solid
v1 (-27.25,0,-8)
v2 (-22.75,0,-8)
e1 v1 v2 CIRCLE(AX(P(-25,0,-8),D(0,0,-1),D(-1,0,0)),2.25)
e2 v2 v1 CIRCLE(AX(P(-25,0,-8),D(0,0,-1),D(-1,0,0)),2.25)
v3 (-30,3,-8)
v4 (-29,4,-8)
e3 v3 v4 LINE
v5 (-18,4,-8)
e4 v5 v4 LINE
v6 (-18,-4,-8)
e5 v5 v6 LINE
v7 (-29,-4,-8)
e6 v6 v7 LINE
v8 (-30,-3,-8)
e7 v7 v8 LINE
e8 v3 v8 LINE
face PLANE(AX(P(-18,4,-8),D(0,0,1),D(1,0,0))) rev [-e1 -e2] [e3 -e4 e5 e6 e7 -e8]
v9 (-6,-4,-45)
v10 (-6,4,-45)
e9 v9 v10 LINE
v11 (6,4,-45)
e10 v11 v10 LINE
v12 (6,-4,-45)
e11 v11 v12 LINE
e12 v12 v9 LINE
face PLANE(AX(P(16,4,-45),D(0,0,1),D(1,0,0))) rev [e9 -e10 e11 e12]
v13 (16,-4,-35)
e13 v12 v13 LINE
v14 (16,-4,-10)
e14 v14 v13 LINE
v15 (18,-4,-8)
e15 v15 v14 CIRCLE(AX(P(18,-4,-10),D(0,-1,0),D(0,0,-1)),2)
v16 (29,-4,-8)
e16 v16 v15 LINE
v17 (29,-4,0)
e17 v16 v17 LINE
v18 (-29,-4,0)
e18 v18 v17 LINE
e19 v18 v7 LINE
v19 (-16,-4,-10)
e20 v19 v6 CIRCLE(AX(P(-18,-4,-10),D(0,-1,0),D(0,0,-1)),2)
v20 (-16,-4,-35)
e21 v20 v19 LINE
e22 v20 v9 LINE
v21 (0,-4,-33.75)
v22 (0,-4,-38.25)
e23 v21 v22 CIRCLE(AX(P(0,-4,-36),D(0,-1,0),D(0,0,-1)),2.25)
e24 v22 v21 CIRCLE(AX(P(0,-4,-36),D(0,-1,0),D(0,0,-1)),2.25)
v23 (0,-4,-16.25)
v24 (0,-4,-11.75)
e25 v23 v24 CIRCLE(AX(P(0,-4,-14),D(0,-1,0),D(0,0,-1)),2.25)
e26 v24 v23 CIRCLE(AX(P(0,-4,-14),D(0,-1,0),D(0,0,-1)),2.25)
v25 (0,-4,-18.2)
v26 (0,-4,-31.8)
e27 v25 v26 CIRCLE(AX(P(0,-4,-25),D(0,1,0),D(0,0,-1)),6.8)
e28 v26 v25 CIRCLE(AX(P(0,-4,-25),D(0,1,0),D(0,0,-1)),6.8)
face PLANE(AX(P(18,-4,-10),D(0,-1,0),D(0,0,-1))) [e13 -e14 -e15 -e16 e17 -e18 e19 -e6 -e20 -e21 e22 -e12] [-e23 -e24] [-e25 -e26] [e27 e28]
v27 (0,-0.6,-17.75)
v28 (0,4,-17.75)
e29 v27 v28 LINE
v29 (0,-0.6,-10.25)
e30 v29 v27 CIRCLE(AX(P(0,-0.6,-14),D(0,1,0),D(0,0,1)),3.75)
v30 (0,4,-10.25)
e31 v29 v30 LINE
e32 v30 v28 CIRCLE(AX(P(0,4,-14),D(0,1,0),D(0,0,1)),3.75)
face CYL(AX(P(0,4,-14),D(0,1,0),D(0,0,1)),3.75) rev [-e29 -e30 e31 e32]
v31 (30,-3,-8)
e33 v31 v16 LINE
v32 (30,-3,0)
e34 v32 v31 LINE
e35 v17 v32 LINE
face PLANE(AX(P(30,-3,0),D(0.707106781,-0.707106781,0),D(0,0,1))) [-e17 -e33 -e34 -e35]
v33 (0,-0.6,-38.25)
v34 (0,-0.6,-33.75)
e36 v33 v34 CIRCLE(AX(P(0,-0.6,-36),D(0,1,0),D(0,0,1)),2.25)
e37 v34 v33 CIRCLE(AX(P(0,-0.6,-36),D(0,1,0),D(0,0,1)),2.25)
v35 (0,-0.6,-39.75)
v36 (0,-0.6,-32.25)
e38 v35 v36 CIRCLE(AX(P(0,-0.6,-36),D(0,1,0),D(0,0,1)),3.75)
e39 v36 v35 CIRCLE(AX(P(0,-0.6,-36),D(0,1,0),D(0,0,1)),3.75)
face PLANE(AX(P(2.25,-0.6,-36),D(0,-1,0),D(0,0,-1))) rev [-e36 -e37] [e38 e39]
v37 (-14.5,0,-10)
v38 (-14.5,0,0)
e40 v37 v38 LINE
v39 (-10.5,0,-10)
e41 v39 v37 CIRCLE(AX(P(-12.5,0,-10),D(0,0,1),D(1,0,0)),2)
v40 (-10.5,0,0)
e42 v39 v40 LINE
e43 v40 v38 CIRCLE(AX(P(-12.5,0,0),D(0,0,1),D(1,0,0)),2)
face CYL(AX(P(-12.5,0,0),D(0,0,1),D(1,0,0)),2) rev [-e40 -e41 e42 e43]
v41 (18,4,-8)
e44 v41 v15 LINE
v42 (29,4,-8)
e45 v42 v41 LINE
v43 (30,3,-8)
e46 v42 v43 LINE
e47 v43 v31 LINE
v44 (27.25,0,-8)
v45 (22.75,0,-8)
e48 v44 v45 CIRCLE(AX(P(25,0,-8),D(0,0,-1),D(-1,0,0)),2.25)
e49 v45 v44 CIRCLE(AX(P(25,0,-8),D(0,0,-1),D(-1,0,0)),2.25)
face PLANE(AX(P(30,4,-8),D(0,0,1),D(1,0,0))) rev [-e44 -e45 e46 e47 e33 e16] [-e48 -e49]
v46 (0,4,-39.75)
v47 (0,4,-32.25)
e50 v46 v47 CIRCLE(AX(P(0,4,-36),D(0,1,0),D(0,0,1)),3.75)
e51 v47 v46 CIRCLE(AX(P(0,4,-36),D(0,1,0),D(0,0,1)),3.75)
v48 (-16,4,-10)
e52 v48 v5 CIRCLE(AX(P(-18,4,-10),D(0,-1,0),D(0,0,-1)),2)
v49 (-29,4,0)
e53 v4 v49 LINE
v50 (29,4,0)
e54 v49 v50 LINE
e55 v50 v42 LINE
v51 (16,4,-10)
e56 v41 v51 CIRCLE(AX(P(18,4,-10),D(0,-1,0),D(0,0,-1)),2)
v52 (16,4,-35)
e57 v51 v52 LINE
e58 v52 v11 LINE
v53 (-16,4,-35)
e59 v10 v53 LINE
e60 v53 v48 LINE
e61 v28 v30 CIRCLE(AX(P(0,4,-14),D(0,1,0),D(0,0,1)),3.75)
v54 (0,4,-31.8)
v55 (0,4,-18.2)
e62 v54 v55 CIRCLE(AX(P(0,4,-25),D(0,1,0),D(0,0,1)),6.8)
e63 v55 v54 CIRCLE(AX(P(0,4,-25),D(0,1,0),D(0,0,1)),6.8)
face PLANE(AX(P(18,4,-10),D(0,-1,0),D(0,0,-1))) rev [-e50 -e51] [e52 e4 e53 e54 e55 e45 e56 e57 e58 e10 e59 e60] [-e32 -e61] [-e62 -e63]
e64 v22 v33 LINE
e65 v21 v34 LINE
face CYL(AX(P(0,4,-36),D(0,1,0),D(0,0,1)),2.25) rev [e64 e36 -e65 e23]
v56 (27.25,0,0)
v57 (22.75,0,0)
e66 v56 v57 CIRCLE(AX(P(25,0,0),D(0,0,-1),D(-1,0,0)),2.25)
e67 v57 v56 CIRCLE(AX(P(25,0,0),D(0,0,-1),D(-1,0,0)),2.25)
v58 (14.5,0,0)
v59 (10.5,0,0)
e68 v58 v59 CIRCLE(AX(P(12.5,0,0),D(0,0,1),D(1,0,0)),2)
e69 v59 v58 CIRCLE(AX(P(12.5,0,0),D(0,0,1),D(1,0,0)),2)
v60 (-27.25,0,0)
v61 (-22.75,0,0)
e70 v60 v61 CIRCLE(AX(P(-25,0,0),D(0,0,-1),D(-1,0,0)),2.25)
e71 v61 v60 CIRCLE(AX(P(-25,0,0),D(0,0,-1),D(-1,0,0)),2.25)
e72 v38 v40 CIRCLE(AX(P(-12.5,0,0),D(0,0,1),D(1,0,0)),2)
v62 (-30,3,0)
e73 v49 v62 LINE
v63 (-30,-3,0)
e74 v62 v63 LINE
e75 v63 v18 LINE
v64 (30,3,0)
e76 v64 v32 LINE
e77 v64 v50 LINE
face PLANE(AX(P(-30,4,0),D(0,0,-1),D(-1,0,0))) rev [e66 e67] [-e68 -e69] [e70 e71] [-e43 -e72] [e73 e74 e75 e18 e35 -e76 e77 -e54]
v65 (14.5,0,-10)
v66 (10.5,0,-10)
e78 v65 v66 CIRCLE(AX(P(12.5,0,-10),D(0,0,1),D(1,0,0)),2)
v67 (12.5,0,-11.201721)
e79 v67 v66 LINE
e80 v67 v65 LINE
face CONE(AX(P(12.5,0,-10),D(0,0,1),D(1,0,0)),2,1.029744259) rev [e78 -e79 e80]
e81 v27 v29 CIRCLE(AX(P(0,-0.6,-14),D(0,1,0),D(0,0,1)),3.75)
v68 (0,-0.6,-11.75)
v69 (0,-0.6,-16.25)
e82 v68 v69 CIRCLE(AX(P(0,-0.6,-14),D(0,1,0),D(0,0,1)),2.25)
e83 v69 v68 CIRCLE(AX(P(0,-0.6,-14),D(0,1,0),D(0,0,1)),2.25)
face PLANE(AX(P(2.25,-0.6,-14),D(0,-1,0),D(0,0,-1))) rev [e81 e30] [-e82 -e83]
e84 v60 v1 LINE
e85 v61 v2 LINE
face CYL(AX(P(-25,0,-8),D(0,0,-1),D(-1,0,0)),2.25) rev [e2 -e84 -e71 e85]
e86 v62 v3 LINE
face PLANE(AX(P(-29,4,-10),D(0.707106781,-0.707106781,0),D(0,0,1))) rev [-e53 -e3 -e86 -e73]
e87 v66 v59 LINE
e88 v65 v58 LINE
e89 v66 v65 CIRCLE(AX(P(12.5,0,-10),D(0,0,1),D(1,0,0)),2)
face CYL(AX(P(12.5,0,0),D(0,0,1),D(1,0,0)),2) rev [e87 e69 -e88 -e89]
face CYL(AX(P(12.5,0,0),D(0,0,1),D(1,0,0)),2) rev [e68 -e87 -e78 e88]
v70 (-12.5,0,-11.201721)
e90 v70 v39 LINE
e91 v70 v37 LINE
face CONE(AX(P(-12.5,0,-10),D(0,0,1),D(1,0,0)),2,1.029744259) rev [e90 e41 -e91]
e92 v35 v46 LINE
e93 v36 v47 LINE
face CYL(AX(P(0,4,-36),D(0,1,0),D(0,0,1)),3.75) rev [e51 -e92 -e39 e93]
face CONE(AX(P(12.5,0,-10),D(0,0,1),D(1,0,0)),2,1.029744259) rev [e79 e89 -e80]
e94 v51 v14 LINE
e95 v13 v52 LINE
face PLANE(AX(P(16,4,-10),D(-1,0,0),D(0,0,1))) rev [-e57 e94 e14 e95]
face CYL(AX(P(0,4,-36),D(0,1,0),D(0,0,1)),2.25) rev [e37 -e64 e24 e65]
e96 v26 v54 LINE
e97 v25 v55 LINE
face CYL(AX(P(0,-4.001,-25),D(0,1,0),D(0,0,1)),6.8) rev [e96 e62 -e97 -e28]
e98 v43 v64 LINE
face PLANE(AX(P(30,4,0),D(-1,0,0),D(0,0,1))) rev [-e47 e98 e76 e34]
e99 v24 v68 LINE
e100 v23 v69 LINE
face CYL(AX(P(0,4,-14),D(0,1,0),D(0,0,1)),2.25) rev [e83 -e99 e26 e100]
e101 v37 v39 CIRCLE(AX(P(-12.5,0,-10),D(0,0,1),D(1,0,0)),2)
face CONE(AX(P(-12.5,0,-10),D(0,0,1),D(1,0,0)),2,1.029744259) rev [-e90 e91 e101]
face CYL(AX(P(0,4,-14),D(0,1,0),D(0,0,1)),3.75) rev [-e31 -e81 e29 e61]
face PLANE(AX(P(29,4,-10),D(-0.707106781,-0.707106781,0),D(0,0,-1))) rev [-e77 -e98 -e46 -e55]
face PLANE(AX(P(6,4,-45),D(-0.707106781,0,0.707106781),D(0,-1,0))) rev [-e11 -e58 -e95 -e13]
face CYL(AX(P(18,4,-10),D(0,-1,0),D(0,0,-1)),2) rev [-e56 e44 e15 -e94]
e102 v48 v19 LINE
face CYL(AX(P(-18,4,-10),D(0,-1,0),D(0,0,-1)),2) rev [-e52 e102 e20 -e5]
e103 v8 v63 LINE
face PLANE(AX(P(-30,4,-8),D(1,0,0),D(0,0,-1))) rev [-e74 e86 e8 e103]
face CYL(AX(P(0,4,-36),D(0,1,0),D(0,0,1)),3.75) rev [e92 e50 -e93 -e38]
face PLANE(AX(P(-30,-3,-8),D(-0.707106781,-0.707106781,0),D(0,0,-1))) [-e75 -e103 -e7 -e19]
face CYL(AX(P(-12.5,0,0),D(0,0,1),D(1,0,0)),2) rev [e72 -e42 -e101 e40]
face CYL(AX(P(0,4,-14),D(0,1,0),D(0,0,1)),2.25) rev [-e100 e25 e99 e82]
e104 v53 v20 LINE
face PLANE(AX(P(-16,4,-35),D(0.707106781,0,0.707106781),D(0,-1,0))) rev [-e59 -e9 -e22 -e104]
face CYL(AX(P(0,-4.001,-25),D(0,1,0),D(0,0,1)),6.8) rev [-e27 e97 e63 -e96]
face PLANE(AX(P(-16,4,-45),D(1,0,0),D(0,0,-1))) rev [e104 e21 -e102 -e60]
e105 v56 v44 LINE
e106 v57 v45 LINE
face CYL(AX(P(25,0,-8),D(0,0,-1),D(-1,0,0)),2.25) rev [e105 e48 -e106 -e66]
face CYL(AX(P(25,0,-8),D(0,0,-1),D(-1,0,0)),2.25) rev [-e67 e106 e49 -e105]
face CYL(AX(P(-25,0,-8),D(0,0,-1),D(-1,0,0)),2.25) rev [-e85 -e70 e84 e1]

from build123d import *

# Parameters (mm, degrees)
EXTRUDE_1_DEPTH              = 4
CHAMFER_1_SIZE               = 1
CHAMFER_2_SIZE               = 10
CUT_EXTRUDE_1_REACH          = 56.672
SKETCH_2_R                   = 6.8
HOLE_WIZARD_M4_2_D           = 4.5
HOLE_WIZARD_M4_2_CBORE_D     = 7.5
HOLE_WIZARD_M4_2_CBORE_DEPTH = 4.6
F_4_0MM_1_D                  = 4
F_4_0MM_1_DEPTH              = 10
F_4_0MM_1_TIP                = 1.201721238
HOLE_WIZARD_M4_1_D           = 4.5


with BuildPart() as part:
    # 草图1 → 凸台-拉伸1 (new, symmetric)
    with BuildSketch(Plane(origin=(0, 0, 0), x_dir=(1, 0, 0), z_dir=(0, 1, 0))):
        with BuildLine():
            Line((-30, 0), (30, 0))
            Line((30, 0), (30, 8))
            Line((30, 8), (18, 8))
            ThreePointArc((18, 8), (16.585786438, 8.585786438), (16, 10))
            Line((16, 10), (16, 45))
            Line((16, 45), (-16, 45))
            Line((-16, 45), (-16, 10))
            ThreePointArc((-16, 10), (-16.585786438, 8.585786438), (-18, 8))
            Line((-18, 8), (-30, 8))
            Line((-30, 8), (-30, 0))
        make_face()
    extrude(amount=EXTRUDE_1_DEPTH, both=True)

    # 倒角1
    chamfer_1_edges = [part.edges().sort_by_distance(p)[0] for p in [
        (30, 4, -4),
        (30, -4, -4),
        (-30, -4, -4),
        (-30, 4, -4),
    ]]
    chamfer(chamfer_1_edges, length=CHAMFER_1_SIZE)

    # 倒角2
    chamfer_2_edges = [part.edges().sort_by_distance(p)[0] for p in [
        (-16, 0, -45),
        (16, 0, -45),
    ]]
    chamfer(chamfer_2_edges, length=CHAMFER_2_SIZE)

    # 草图2 → 切除-拉伸1 (cut, up to next)
    with BuildSketch(Plane(origin=(0, 4, 0), x_dir=(1, 0, 0), z_dir=(0, 1, 0)), mode=Mode.PRIVATE) as cut_extrude_1_sk1:
        with Locations(Location((0, 25, 0), (0, 0, 270))):
            Circle(SKETCH_2_R)
    cut_extrude_1_tool1 = extrude(cut_extrude_1_sk1.sketch, amount=-CUT_EXTRUDE_1_REACH, mode=Mode.PRIVATE) & part.part
    add(cut_extrude_1_tool1.solids().sort_by_distance((0, 4, -25))[0], mode=Mode.SUBTRACT)

    # M4 六角圆柱头螺钉的柱形沉头孔2 (through all)
    with Locations(Plane(origin=(0, 4, 0), x_dir=(1, 0, 0), z_dir=(0, 1, 0))):
        with Locations((0, 36), (0, 14)):
            CounterBoreHole(HOLE_WIZARD_M4_2_D / 2, HOLE_WIZARD_M4_2_CBORE_D / 2, HOLE_WIZARD_M4_2_CBORE_DEPTH)

    # Ø4.0mm 暗销孔1
    with Locations(Plane.XY):
        with Locations((-12.5, 0), (12.5, 0)):
            Hole(F_4_0MM_1_D / 2, depth=F_4_0MM_1_DEPTH)
            with Locations((0, 0, -(F_4_0MM_1_DEPTH + F_4_0MM_1_TIP / 2))):  # 118° drill point
                Cone(0, F_4_0MM_1_D / 2, F_4_0MM_1_TIP, mode=Mode.SUBTRACT)

    # M4 间隙孔1 (through all)
    with Locations(Plane(origin=(0, 0, -8), x_dir=(-1, 0, 0), z_dir=(0, 0, -1))):
        with Locations((-25, 0), (25, 0)):
            Hole(HOLE_WIZARD_M4_1_D / 2)


solid = part.part
